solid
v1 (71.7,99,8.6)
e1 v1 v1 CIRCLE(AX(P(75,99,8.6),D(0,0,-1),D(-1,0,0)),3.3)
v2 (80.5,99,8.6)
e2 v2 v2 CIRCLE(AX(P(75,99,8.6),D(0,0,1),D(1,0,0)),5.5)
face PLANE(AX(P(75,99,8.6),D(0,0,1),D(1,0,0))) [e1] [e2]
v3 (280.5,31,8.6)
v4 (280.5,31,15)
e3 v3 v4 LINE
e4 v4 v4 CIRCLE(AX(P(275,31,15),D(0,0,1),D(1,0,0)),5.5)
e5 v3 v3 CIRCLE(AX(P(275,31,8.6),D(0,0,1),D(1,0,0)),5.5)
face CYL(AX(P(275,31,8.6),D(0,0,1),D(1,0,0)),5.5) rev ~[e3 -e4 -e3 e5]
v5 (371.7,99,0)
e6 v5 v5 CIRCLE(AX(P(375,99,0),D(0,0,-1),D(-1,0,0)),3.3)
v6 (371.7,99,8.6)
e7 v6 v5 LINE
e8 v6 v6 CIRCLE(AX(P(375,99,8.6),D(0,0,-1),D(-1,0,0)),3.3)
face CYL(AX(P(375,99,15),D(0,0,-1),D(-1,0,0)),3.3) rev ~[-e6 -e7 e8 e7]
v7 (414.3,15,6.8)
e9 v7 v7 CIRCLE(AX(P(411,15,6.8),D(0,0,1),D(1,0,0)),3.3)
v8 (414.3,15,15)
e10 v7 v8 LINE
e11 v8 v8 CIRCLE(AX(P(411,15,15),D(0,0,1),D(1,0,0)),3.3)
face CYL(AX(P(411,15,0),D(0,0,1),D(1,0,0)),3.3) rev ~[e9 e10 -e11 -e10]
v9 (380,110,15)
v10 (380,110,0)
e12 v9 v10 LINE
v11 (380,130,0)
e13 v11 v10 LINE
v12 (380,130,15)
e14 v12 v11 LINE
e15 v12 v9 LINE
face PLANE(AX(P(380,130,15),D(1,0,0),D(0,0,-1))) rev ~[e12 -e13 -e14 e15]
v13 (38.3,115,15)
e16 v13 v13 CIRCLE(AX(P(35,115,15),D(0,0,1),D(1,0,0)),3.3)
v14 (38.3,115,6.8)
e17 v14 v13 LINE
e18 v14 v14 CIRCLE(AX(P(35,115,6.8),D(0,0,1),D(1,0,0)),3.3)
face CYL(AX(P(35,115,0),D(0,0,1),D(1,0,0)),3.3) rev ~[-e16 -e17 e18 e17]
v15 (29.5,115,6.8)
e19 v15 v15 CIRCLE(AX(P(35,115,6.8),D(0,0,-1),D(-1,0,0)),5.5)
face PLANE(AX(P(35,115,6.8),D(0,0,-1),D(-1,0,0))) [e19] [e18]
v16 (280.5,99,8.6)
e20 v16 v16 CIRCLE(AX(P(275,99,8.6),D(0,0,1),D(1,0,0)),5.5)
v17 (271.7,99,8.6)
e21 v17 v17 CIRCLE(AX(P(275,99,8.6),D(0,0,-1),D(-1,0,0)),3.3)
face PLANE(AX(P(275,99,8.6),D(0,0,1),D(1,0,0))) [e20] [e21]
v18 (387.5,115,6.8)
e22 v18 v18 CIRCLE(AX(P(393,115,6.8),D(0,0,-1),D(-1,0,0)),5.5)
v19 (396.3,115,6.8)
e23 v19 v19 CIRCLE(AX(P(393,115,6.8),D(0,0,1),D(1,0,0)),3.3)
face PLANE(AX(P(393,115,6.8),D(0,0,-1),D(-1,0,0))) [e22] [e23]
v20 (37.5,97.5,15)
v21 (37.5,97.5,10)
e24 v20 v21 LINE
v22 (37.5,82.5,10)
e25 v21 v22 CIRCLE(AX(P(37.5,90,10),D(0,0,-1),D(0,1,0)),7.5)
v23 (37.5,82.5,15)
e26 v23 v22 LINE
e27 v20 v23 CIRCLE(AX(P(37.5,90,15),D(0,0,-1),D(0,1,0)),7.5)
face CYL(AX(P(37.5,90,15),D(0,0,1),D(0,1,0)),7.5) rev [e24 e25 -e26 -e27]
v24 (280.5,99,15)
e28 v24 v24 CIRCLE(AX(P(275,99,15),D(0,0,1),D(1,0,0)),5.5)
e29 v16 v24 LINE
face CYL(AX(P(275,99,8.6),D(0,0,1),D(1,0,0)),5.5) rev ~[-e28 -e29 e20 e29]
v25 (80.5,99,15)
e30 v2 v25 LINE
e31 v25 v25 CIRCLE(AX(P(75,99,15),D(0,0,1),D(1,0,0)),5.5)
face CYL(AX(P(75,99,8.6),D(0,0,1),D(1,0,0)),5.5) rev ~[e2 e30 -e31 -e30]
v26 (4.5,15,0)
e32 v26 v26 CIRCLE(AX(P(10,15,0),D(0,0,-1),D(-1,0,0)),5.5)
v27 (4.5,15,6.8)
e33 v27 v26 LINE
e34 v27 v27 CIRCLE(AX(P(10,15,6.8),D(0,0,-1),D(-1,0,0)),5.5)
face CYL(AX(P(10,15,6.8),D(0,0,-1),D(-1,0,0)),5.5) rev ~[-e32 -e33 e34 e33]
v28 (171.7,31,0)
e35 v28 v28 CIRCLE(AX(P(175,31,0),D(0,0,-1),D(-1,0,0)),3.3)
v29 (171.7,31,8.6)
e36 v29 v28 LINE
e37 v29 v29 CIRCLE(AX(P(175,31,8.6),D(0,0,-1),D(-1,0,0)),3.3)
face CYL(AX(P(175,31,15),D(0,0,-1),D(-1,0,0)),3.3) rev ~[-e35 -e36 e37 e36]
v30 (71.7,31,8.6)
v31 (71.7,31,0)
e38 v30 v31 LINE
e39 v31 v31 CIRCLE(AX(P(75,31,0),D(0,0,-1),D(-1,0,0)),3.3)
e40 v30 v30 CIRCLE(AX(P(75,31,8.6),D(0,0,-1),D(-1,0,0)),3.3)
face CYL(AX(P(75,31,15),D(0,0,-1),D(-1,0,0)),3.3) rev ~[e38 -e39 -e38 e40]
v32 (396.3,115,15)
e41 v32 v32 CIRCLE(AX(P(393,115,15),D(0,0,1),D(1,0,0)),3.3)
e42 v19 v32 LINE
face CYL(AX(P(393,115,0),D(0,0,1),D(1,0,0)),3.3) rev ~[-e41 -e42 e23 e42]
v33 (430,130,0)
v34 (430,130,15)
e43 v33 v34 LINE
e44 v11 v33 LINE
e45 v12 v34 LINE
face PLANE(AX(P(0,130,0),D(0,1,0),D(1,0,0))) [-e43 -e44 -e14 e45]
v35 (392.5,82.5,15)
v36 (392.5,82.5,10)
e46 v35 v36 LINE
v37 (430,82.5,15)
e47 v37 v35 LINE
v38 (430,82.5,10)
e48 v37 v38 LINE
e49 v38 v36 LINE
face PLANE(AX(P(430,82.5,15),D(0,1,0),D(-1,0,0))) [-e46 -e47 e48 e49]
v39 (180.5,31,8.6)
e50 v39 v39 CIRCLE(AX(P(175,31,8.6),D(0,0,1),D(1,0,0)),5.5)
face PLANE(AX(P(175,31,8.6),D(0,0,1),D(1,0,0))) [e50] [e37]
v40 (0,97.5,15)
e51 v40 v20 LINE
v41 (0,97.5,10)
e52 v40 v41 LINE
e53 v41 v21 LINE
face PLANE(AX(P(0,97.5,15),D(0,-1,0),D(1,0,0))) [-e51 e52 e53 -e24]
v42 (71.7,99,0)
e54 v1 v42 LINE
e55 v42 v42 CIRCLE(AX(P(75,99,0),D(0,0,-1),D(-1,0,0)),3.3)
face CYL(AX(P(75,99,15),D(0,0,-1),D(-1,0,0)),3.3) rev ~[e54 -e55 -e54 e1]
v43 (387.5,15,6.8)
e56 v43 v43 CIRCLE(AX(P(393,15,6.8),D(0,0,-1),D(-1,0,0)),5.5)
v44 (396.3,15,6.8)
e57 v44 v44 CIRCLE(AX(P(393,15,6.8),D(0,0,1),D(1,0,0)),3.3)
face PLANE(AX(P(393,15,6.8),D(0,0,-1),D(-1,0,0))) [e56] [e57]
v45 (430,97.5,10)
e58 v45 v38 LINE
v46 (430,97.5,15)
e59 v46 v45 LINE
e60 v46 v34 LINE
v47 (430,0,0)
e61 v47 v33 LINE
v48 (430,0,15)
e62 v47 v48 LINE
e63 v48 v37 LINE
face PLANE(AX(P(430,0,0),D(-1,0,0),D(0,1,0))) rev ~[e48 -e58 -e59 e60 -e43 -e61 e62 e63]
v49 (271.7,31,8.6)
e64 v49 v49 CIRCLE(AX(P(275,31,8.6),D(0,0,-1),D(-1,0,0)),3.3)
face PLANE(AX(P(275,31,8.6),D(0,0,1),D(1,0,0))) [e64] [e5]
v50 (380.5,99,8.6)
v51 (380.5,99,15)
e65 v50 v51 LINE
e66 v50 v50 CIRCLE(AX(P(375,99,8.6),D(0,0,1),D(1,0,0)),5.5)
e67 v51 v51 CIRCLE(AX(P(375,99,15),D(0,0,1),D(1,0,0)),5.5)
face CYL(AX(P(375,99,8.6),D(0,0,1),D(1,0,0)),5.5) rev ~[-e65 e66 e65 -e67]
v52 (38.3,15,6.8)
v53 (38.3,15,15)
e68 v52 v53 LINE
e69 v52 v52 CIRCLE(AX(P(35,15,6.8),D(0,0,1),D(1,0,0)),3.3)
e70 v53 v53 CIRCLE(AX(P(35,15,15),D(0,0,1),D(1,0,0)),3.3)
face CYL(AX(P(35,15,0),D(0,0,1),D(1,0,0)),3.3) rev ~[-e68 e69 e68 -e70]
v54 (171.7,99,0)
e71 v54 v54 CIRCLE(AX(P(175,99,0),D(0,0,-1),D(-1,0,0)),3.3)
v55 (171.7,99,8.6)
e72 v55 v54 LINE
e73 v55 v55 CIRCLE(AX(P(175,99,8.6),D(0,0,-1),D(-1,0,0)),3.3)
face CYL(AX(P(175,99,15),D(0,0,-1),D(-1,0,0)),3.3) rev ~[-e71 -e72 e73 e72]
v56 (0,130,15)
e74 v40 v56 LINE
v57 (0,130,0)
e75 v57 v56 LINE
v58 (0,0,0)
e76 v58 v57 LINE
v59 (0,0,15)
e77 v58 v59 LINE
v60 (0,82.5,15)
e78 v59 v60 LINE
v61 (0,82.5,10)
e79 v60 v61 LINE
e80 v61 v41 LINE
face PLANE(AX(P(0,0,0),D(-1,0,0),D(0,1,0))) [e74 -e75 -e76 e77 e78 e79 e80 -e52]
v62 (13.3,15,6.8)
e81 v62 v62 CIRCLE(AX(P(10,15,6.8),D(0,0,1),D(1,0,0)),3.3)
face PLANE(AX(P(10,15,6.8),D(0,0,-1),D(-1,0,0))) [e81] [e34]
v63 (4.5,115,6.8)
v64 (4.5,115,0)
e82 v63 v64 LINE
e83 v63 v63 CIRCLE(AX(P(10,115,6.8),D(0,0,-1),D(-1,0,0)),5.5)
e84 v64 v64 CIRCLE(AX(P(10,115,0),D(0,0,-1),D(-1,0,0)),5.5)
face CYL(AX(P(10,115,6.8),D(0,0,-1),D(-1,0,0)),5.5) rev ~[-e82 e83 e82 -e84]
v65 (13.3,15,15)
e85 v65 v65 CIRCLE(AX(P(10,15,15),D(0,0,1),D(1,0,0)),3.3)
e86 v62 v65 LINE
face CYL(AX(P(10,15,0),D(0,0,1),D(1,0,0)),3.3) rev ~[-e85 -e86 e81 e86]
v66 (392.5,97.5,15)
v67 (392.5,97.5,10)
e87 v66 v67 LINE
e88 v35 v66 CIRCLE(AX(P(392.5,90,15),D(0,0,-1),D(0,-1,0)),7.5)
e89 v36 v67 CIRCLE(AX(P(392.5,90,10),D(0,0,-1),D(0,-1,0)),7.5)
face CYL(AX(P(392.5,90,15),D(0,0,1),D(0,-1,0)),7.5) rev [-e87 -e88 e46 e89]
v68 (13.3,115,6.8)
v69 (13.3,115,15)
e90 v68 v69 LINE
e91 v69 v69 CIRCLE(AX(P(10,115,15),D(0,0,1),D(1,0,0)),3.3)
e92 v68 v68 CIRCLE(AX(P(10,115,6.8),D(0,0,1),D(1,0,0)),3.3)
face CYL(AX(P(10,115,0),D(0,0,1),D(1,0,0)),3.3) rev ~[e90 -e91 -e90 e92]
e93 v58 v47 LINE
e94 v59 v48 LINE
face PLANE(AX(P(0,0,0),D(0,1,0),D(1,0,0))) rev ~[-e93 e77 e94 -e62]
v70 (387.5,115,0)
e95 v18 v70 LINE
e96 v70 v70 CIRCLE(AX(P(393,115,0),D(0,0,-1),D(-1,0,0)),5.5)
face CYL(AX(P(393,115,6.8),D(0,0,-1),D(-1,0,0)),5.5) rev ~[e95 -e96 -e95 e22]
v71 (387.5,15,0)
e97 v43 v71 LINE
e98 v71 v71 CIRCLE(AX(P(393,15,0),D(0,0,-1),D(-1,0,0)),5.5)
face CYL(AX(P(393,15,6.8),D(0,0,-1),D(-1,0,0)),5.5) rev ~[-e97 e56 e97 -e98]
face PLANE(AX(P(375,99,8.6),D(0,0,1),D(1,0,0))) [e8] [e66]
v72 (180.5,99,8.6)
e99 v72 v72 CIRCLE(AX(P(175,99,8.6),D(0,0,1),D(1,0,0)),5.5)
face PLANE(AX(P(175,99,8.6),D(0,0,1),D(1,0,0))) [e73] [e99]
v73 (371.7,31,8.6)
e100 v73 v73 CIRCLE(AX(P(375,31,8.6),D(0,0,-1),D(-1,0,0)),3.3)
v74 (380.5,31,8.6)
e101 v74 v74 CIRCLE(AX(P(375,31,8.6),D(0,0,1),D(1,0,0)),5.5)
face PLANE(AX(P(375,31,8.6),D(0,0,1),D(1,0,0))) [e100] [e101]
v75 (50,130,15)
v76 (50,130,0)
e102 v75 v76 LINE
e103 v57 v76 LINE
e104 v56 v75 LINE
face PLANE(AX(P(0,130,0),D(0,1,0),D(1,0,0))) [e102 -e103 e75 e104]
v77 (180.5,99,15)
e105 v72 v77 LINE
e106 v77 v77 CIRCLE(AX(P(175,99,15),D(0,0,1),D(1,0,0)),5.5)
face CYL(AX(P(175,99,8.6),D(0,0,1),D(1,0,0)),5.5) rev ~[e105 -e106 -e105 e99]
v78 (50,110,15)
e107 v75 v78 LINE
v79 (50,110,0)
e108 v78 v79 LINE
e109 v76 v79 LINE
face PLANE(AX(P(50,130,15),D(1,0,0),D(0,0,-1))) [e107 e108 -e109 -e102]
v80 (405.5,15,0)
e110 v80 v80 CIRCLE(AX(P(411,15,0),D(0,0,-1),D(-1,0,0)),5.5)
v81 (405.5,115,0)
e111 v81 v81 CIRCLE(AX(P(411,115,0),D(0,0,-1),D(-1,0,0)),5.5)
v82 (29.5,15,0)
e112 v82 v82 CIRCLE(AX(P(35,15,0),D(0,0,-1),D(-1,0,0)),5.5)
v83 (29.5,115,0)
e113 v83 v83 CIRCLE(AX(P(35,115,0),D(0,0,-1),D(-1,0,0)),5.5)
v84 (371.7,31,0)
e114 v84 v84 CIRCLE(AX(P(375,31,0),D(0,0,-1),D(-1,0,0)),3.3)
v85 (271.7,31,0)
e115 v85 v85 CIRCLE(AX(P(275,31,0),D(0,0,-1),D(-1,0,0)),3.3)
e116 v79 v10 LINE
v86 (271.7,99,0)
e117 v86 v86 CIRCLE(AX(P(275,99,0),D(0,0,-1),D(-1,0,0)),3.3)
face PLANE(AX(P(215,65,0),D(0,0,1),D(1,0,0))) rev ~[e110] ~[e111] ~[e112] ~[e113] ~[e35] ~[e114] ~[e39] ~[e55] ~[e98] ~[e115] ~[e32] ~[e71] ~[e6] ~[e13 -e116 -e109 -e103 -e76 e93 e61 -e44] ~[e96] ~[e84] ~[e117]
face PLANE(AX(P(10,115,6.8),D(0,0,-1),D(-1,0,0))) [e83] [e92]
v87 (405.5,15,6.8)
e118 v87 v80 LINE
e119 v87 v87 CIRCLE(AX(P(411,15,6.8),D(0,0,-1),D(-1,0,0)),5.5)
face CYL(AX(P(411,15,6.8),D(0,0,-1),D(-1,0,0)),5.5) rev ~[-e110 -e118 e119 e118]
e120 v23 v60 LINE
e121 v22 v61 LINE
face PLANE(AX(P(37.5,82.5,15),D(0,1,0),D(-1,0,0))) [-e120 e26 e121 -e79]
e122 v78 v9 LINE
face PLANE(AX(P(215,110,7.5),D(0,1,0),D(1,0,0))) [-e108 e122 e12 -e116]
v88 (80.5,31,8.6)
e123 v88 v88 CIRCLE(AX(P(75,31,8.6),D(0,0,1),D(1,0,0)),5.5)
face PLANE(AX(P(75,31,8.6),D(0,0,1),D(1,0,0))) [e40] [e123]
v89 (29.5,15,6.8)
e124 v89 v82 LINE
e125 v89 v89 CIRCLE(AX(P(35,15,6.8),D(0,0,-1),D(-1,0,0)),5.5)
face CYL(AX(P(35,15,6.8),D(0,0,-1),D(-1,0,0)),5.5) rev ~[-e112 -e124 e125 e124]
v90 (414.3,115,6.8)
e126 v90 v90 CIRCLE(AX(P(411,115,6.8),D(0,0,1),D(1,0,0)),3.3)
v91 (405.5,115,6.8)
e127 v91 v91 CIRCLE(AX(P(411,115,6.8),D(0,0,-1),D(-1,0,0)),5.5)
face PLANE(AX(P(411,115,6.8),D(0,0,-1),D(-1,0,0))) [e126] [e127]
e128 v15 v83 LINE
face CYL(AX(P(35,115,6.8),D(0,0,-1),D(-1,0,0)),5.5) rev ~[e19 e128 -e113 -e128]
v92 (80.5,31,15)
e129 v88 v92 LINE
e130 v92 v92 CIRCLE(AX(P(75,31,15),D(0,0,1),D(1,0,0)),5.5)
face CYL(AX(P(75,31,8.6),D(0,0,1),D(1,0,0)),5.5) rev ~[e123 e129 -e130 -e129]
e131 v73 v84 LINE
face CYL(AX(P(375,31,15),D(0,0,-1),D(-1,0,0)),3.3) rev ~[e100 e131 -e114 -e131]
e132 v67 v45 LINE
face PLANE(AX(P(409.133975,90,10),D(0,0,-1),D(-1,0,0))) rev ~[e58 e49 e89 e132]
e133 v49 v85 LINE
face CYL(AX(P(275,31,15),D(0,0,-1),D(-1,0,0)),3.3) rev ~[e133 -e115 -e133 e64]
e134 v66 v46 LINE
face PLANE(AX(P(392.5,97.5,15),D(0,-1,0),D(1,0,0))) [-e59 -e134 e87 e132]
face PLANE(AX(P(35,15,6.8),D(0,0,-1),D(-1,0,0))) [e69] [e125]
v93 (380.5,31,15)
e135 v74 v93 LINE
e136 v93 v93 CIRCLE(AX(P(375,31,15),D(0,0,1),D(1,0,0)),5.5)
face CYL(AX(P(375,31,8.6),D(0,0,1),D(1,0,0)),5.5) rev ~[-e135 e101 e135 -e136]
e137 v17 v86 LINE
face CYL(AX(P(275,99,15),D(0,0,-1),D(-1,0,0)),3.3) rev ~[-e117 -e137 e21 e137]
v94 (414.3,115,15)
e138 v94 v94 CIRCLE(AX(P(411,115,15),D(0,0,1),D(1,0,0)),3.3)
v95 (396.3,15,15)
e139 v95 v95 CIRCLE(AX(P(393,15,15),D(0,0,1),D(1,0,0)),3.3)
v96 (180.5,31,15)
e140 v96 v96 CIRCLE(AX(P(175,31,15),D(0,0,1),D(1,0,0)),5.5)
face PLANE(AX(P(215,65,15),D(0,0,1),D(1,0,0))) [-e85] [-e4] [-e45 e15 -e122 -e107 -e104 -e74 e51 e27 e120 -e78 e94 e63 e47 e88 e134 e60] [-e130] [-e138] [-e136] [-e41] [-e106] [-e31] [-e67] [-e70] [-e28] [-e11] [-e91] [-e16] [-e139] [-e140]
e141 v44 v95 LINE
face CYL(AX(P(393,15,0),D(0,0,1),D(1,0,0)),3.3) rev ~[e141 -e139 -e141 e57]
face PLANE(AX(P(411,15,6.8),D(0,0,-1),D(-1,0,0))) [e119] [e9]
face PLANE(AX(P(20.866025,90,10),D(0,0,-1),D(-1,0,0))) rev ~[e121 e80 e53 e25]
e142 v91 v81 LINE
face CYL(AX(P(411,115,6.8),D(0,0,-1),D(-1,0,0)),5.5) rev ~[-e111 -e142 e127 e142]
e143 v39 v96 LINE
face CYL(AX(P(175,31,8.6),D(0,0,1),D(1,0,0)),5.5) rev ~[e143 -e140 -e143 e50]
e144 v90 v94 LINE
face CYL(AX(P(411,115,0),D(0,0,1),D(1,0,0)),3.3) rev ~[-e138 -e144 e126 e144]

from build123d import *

# Parameters (mm, degrees)
SKETCH1_W                                            = 430
SKETCH1_H                                            = 130
BOSS_EXTRUDE1_DEPTH                                  = 15
HOLE_SIZE_PER_SOCKET_HEAD_CAP_SCREW_TYPE_D           = 6.6
HOLE_SIZE_PER_SOCKET_HEAD_CAP_SCREW_TYPE_CBORE_D     = 11
HOLE_SIZE_PER_SOCKET_HEAD_CAP_SCREW_TYPE_CBORE_DEPTH = 6.8
CUT_EXTRUDE1_DEPTH                                   = 5
CBORE_FOR_M6_HEX_SOCKET_HEAD_CAP_SCREW1_D            = 6.6
CBORE_FOR_M6_HEX_SOCKET_HEAD_CAP_SCREW1_CBORE_D      = 11
CBORE_FOR_M6_HEX_SOCKET_HEAD_CAP_SCREW1_CBORE_DEPTH  = 6.4
SKETCH8_W                                            = 330
SKETCH8_H                                            = 15
CUT_EXTRUDE2_DEPTH                                   = 20


with BuildPart() as part:
    # Sketch1 → Boss-Extrude1 (new body)
    with BuildSketch(Plane.XY):
        with Locations((215, 65)):
            Rectangle(SKETCH1_W, SKETCH1_H)
    extrude(amount=BOSS_EXTRUDE1_DEPTH)

    # Hole size per socket head cap screw type 0 (through all)
    with Locations(Plane(origin=(0, 0, 0), x_dir=(-1, 0, 0), z_dir=(0, 0, -1))):
        with Locations((-10, 15), (-10, 115), (-35, 15), (-35, 115), (-393, 15), (-411, 15), (-393, 115), (-411, 115)):
            CounterBoreHole(HOLE_SIZE_PER_SOCKET_HEAD_CAP_SCREW_TYPE_D / 2, HOLE_SIZE_PER_SOCKET_HEAD_CAP_SCREW_TYPE_CBORE_D / 2, HOLE_SIZE_PER_SOCKET_HEAD_CAP_SCREW_TYPE_CBORE_DEPTH)

    # Sketch5 → Cut-Extrude1 (cut)
    with BuildSketch(Plane.XY.offset(15)):
        with BuildLine():
            Line((430, 97.5), (430, 82.5))
            Line((430, 82.5), (392.5, 82.5))
            ThreePointArc((392.5, 82.5), (385, 90), (392.5, 97.5))
            Line((392.5, 97.5), (430, 97.5))
        make_face()
        with BuildLine():
            Line((37.5, 82.5), (0, 82.5))
            Line((0, 82.5), (0, 97.5))
            Line((0, 97.5), (37.5, 97.5))
            ThreePointArc((37.5, 97.5), (45, 90), (37.5, 82.5))
        make_face()
    extrude(amount=-CUT_EXTRUDE1_DEPTH, mode=Mode.SUBTRACT)

    # CBORE for M6 Hex Socket Head Cap Screw1 (through all)
    with Locations(Plane.XY.offset(15)):
        with Locations((75, 99), (175, 99), (75, 31), (175, 31), (275, 99), (275, 31), (375, 99), (375, 31)):
            CounterBoreHole(CBORE_FOR_M6_HEX_SOCKET_HEAD_CAP_SCREW1_D / 2, CBORE_FOR_M6_HEX_SOCKET_HEAD_CAP_SCREW1_CBORE_D / 2, CBORE_FOR_M6_HEX_SOCKET_HEAD_CAP_SCREW1_CBORE_DEPTH)

    # Sketch8 → Cut-Extrude2 (cut)
    with BuildSketch(Plane(origin=(0, 130, 0), x_dir=(1, 0, 0), z_dir=(0, 1, 0))):
        with Locations((215, -7.5)):
            Rectangle(SKETCH8_W, SKETCH8_H)
    extrude(amount=-CUT_EXTRUDE2_DEPTH, mode=Mode.SUBTRACT)


solid = part.part
